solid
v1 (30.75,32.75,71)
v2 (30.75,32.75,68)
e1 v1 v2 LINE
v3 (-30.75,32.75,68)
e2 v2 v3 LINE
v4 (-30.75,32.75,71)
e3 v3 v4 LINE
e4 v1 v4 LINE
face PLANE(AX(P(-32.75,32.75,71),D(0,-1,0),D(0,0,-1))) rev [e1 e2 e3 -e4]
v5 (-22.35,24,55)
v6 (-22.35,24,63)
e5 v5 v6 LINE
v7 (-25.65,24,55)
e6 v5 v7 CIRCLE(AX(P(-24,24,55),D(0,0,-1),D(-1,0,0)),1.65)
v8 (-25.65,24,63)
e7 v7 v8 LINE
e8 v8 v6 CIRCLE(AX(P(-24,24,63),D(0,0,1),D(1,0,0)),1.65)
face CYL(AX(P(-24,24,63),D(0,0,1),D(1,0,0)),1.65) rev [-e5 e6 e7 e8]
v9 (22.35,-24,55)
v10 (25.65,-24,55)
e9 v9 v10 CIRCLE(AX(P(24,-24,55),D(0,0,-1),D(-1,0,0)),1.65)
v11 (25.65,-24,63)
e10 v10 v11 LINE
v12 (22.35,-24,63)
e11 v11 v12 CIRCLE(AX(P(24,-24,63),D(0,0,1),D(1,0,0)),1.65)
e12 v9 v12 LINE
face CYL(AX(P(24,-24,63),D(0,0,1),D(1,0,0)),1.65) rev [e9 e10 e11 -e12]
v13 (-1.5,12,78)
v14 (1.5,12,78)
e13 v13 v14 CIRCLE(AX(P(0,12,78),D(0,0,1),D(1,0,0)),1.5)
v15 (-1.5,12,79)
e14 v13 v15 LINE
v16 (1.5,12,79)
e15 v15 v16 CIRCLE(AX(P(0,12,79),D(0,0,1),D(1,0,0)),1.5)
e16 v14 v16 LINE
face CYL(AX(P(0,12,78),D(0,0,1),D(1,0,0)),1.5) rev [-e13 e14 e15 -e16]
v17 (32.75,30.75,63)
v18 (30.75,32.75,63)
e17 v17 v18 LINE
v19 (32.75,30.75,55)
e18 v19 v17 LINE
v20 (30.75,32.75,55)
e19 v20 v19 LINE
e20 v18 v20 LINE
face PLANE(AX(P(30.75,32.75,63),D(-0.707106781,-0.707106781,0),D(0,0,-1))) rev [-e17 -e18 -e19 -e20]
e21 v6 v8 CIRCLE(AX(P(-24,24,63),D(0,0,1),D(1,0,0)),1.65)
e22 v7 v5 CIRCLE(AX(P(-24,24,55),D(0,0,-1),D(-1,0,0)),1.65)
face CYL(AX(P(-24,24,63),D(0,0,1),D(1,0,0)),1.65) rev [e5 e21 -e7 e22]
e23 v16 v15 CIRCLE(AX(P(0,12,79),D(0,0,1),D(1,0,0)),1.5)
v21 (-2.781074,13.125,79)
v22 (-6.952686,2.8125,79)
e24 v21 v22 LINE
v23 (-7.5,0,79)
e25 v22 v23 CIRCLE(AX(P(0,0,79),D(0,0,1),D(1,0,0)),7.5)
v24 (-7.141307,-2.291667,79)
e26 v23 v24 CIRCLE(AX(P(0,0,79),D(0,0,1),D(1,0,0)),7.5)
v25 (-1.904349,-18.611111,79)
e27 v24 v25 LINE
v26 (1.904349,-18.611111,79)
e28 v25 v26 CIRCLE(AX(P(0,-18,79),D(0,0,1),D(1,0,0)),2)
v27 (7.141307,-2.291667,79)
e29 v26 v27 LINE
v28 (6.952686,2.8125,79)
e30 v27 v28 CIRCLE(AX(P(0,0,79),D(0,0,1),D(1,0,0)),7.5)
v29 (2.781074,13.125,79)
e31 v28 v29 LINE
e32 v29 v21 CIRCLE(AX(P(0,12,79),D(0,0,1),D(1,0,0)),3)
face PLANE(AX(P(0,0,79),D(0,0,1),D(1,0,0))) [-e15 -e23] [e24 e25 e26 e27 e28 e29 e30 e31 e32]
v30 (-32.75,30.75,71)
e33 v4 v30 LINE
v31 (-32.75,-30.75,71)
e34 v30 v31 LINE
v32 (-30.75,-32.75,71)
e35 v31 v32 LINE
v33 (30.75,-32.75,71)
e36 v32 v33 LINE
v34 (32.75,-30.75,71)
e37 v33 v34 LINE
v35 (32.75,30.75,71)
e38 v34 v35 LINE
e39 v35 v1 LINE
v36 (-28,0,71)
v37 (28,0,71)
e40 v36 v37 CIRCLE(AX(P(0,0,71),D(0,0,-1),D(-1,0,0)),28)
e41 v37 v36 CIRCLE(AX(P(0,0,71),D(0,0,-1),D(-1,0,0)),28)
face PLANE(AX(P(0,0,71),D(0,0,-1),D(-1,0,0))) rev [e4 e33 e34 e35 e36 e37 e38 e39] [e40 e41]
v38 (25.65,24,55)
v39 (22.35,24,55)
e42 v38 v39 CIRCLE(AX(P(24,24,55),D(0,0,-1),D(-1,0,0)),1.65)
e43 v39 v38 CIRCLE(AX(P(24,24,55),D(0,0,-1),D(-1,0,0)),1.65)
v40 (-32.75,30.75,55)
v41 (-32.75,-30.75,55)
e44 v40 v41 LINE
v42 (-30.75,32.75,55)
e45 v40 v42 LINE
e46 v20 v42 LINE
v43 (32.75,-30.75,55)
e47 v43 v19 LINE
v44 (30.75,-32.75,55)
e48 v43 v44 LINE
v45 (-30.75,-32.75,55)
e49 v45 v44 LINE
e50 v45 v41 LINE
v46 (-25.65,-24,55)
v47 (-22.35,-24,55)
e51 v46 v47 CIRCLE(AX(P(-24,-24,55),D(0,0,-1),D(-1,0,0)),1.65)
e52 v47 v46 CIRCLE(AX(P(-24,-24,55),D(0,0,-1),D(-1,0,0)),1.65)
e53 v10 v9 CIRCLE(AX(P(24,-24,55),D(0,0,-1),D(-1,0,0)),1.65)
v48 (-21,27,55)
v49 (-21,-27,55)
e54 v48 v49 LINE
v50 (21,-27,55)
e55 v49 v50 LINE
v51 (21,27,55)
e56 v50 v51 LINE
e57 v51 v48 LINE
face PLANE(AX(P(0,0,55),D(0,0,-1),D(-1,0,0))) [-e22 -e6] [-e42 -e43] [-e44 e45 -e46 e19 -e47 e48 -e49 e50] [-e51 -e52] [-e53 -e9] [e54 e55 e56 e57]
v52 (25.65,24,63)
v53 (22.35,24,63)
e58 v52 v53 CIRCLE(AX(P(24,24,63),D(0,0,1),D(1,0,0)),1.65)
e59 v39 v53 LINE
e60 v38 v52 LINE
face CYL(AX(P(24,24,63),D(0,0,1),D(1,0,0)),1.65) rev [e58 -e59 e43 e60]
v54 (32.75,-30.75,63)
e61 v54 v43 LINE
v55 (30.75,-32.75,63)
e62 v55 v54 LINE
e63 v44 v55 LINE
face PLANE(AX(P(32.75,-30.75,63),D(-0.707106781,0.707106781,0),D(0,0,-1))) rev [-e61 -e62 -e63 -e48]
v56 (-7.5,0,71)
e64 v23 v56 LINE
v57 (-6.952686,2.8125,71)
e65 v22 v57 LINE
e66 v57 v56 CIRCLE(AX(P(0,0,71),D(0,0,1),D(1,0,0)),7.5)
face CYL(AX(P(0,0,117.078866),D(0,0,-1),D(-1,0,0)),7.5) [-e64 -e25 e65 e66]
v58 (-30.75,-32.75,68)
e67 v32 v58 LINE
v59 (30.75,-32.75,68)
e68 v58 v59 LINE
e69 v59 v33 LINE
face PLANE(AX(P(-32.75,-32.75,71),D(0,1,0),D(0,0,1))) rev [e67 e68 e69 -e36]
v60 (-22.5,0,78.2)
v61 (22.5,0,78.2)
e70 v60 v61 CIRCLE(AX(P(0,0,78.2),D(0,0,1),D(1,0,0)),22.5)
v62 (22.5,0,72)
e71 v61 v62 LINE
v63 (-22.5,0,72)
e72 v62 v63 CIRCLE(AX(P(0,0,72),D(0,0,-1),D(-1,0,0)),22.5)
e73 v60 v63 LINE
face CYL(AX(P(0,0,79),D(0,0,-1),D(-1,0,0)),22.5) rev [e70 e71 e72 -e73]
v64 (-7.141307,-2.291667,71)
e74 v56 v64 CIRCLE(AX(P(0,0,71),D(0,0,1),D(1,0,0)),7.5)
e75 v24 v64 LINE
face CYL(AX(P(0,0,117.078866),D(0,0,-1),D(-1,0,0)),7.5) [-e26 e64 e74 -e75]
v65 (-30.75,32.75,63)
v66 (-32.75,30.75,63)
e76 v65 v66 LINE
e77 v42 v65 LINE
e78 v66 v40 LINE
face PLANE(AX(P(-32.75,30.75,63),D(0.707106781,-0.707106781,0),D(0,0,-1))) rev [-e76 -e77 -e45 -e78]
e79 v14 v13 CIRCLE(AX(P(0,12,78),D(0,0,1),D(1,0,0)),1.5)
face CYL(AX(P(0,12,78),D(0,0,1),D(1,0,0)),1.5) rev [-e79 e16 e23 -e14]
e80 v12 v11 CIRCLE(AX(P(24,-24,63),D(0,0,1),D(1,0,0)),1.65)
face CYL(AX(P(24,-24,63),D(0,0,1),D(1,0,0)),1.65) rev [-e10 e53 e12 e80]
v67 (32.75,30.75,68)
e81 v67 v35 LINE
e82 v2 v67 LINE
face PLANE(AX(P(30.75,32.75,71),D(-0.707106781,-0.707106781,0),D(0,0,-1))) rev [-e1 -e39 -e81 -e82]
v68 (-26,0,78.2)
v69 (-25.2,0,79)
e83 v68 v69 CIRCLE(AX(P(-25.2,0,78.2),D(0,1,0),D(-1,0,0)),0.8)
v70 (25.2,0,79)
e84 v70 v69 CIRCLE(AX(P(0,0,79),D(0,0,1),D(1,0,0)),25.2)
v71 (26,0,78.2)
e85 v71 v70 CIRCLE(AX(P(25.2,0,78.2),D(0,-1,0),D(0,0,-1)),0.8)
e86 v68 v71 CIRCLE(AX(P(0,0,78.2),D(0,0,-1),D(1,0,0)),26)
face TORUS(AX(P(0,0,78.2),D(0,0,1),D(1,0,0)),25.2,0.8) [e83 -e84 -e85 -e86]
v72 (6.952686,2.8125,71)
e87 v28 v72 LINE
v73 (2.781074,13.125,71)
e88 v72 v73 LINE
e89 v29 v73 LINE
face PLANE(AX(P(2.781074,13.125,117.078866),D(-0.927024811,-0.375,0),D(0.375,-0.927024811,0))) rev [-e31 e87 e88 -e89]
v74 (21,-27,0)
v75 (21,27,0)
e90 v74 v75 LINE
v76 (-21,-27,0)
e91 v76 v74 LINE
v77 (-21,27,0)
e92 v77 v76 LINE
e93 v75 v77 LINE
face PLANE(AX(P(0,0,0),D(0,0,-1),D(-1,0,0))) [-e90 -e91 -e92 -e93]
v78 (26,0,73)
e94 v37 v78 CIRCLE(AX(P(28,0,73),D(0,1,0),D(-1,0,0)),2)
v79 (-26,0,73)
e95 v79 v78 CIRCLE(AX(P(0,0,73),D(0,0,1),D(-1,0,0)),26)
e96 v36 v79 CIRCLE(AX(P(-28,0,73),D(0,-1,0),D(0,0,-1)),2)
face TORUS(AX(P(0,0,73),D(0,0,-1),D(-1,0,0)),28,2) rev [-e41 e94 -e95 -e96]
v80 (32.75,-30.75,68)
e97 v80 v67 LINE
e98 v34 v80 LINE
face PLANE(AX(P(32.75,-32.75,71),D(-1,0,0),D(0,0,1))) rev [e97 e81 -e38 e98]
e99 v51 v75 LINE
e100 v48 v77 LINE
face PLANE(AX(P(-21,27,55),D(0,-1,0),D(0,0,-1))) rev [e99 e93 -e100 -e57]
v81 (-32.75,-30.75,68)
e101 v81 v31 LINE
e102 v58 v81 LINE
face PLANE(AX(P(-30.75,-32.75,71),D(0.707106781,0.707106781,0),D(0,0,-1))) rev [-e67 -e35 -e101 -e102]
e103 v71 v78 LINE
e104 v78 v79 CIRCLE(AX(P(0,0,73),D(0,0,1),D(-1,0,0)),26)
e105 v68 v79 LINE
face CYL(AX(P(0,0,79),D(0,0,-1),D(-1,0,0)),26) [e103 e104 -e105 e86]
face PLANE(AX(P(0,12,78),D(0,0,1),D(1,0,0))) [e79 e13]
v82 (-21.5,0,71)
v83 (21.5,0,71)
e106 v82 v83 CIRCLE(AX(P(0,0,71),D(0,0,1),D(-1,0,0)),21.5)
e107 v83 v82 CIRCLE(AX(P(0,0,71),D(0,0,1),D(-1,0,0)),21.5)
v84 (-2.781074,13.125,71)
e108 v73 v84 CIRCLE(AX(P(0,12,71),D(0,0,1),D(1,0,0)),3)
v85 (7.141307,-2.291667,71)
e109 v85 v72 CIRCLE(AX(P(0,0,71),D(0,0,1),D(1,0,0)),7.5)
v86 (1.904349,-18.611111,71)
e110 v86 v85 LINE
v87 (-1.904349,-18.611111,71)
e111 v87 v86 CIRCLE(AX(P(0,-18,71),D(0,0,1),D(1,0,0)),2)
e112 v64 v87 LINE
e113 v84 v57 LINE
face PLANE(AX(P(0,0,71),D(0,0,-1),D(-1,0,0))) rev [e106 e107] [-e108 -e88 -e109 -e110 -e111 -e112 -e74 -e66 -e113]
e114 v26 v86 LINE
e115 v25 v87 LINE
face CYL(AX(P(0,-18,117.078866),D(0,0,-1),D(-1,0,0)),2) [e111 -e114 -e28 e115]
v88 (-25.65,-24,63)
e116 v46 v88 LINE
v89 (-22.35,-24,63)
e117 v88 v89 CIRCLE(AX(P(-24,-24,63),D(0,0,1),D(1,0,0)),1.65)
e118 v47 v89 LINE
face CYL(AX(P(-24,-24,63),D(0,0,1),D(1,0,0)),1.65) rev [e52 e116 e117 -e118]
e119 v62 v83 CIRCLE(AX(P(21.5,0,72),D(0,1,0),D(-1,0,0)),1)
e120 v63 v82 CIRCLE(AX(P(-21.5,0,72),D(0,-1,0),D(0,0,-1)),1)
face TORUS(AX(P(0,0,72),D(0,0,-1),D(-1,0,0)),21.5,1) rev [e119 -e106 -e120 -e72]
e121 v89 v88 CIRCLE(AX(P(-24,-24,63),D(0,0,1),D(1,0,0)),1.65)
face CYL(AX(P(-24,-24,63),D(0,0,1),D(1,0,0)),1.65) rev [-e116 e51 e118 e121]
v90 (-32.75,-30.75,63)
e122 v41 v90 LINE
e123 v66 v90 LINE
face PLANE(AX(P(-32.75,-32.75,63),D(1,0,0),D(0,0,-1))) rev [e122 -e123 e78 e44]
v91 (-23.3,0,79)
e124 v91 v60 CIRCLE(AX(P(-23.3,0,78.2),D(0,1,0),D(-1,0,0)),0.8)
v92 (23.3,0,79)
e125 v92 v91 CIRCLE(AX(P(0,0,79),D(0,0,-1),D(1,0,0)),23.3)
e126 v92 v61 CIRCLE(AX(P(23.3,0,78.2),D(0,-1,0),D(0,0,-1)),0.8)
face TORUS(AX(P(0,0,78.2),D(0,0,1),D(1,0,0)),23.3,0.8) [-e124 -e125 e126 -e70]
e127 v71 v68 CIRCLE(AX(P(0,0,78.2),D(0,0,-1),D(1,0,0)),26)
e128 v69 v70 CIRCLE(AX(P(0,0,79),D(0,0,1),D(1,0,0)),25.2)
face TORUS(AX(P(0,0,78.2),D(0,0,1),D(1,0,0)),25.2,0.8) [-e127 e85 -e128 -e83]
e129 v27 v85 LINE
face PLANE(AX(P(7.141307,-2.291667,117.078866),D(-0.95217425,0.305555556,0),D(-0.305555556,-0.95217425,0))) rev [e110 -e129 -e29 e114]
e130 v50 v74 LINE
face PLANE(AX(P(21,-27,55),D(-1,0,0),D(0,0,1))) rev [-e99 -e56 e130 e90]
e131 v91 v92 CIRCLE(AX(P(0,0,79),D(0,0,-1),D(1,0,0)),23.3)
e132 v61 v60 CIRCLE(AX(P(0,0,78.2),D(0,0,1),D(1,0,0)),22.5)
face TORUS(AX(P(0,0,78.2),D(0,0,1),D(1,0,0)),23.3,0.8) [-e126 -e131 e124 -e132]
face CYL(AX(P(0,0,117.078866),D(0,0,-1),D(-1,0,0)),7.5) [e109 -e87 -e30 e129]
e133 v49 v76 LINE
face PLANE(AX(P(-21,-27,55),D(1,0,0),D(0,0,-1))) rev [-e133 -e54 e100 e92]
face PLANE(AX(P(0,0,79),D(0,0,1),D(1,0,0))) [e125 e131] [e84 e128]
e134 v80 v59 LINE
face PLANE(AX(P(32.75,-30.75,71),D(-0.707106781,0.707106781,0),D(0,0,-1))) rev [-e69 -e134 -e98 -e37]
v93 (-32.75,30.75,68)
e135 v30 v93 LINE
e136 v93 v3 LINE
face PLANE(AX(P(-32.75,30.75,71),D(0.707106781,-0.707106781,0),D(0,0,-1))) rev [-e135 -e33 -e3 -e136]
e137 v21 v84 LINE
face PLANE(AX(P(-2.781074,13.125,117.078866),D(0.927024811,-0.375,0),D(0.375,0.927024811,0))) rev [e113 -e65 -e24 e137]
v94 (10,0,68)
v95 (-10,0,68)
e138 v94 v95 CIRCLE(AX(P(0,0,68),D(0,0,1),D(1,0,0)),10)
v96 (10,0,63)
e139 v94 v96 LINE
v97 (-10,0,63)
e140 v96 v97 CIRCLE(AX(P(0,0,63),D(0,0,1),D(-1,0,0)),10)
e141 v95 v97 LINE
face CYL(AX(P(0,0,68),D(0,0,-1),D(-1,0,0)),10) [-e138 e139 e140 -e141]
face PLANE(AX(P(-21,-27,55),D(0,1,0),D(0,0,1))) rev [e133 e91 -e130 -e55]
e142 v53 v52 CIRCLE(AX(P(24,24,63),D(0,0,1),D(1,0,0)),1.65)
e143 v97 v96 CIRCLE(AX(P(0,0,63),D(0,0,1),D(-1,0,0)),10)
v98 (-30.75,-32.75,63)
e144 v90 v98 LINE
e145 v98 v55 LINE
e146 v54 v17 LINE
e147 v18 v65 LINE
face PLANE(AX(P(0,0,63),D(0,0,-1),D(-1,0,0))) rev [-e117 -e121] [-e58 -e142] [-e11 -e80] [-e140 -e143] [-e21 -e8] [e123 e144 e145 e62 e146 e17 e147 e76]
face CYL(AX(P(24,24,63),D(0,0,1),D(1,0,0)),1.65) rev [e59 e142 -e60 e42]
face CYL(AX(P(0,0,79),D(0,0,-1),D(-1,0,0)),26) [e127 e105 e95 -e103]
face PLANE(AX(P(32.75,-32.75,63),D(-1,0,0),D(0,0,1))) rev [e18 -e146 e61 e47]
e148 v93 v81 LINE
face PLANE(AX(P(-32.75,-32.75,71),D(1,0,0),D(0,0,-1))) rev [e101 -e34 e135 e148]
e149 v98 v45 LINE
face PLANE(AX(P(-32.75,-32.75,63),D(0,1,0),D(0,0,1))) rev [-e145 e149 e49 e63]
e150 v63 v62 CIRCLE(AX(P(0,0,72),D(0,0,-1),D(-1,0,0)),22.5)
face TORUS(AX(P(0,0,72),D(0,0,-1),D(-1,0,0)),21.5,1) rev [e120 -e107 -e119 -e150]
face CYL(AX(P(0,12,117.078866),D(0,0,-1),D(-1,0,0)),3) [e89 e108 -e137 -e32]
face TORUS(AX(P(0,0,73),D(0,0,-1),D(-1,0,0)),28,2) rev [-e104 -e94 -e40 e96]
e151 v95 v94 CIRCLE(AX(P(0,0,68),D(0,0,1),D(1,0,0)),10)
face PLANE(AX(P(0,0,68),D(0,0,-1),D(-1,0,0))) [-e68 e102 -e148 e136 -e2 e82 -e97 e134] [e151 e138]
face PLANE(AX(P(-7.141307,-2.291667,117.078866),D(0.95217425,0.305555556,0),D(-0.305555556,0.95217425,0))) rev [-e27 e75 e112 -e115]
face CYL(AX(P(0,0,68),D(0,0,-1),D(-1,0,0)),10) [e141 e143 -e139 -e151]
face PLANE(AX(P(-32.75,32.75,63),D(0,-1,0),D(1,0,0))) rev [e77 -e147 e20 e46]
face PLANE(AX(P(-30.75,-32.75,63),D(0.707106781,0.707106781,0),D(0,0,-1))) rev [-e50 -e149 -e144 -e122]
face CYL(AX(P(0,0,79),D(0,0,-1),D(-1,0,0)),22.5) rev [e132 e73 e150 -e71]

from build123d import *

# Parameters (mm, degrees)
SKETCH_1_W             = 42
SKETCH_1_H             = 54
EXTRUDE_1_DEPTH        = 55
SKETCH_5_W             = 65.5
SKETCH_5_H             = 65.5
EXTRUDE_3_DEPTH        = 8
SKETCH_6_R             = 10
EXTRUDE_4_DEPTH        = 5
HOLE_WIZARD_M4_1_D     = 3.3
HOLE_WIZARD_M4_1_DEPTH = 11.5
HOLE_WIZARD_M4_1_TIP   = 0.991420021
CHAMFER_1_SIZE         = 2
SKETCH_9_W             = 65.5
SKETCH_9_H             = 65.5
EXTRUDE_5_DEPTH        = 3
SKETCH_10_R            = 26
SKETCH_10_R_2          = 22.5
EXTRUDE_6_DEPTH        = 8
EXTRUDE_7_DEPTH        = 8
FILLET_1_R             = 2
FILLET_2_R             = 1
FILLET_3_R             = 0.8
SKETCH_12_R            = 1.5
CUT_EXTRUDE_1_DEPTH    = 1
CHAMFER_2_SIZE         = 2


with BuildPart() as part:
    # 草图1 → 凸台-拉伸1 (new body)
    with BuildSketch(Plane.XY):
        Rectangle(SKETCH_1_W, SKETCH_1_H)
    extrude(amount=EXTRUDE_1_DEPTH)

    # 草图5 → 凸台-拉伸3 (add)
    with BuildSketch(Plane.XY.offset(55)):
        Rectangle(SKETCH_5_W, SKETCH_5_H)
    extrude(amount=EXTRUDE_3_DEPTH)

    # 草图6 → 凸台-拉伸4 (add)
    with BuildSketch(Plane.XY.offset(63)):
        with Locations(Location((0, 0, 0), (0, 0, 180))):
            Circle(SKETCH_6_R)
    extrude(amount=EXTRUDE_4_DEPTH)

    # M4 螺纹孔1
    with Locations(Plane.XY.offset(63)):
        with Locations((-24, 24), (24, 24), (24, -24), (-24, -24)):
            Hole(HOLE_WIZARD_M4_1_D / 2, depth=HOLE_WIZARD_M4_1_DEPTH)
            with Locations((0, 0, -(HOLE_WIZARD_M4_1_DEPTH + HOLE_WIZARD_M4_1_TIP / 2))):  # 118° drill point
                Cone(0, HOLE_WIZARD_M4_1_D / 2, HOLE_WIZARD_M4_1_TIP, mode=Mode.SUBTRACT)

    # 倒角1
    chamfer_1_edges = [part.edges().sort_by_distance(p)[0] for p in [
        (32.75, -32.75, 59),
        (32.75, 32.75, 59),
        (-32.75, 32.75, 59),
        (-32.75, -32.75, 59),
    ]]
    chamfer(chamfer_1_edges, length=CHAMFER_1_SIZE)

    # 草图9 → 凸台-拉伸5 (add)
    with BuildSketch(Plane.XY.offset(68)):
        Rectangle(SKETCH_9_W, SKETCH_9_H)
    extrude(amount=EXTRUDE_5_DEPTH)

    # 草图10 → 凸台-拉伸6 (add)
    with BuildSketch(Plane.XY.offset(71)):
        with Locations(Location((0, 0, 0), (0, 0, 180))):
            Circle(SKETCH_10_R)
        Circle(SKETCH_10_R_2, mode=Mode.SUBTRACT)
    extrude(amount=EXTRUDE_6_DEPTH)

    # 草图11 → 凸台-拉伸7 (add)
    with BuildSketch(Plane.XY.offset(71)):
        with BuildLine():
            Line((2.781074433, 13.125), (6.952686082, 2.8125))
            ThreePointArc((6.952686082, 2.8125), (7.494884169, 0.276968033), (7.141306875, -2.291666667))
            Line((7.141306875, -2.291666667), (1.9043485, -18.611111111))
            ThreePointArc((1.9043485, -18.611111111), (0, -20), (-1.9043485, -18.611111111))
            Line((-1.9043485, -18.611111111), (-7.141306875, -2.291666667))
            ThreePointArc((-7.141306875, -2.291666667), (-7.494884169, 0.276968033), (-6.952686082, 2.8125))
            Line((-6.952686082, 2.8125), (-2.781074433, 13.125))
            ThreePointArc((-2.781074433, 13.125), (0, 15), (2.781074433, 13.125))
        make_face()
    extrude(amount=EXTRUDE_7_DEPTH)

    # 圆角1
    fillet_1_edges = [part.edges().sort_by_distance(p)[0] for p in [
        (26, 0, 71),
    ]]
    fillet(fillet_1_edges, radius=FILLET_1_R)

    # 圆角2
    fillet_2_edges = [part.edges().sort_by_distance(p)[0] for p in [
        (-22.5, 0, 71),
    ]]
    fillet(fillet_2_edges, radius=FILLET_2_R)

    # 圆角3
    fillet_3_edges = [part.edges().sort_by_distance(p)[0] for p in [
        (26, 0, 79),
        (-22.5, 0, 79),
    ]]
    fillet(fillet_3_edges, radius=FILLET_3_R)

    # 草图12 → 切除-拉伸1 (cut)
    with BuildSketch(Plane.XY.offset(79)):
        with Locations((0, 12)):
            Circle(SKETCH_12_R)
    extrude(amount=-CUT_EXTRUDE_1_DEPTH, mode=Mode.SUBTRACT)

    # 倒角2
    chamfer_2_edges = [part.edges().sort_by_distance(p)[0] for p in [
        (32.75, -32.75, 69.5),
        (32.75, 32.75, 69.5),
        (-32.75, 32.75, 69.5),
        (-32.75, -32.75, 69.5),
    ]]
    chamfer(chamfer_2_edges, length=CHAMFER_2_SIZE)


solid = part.part
